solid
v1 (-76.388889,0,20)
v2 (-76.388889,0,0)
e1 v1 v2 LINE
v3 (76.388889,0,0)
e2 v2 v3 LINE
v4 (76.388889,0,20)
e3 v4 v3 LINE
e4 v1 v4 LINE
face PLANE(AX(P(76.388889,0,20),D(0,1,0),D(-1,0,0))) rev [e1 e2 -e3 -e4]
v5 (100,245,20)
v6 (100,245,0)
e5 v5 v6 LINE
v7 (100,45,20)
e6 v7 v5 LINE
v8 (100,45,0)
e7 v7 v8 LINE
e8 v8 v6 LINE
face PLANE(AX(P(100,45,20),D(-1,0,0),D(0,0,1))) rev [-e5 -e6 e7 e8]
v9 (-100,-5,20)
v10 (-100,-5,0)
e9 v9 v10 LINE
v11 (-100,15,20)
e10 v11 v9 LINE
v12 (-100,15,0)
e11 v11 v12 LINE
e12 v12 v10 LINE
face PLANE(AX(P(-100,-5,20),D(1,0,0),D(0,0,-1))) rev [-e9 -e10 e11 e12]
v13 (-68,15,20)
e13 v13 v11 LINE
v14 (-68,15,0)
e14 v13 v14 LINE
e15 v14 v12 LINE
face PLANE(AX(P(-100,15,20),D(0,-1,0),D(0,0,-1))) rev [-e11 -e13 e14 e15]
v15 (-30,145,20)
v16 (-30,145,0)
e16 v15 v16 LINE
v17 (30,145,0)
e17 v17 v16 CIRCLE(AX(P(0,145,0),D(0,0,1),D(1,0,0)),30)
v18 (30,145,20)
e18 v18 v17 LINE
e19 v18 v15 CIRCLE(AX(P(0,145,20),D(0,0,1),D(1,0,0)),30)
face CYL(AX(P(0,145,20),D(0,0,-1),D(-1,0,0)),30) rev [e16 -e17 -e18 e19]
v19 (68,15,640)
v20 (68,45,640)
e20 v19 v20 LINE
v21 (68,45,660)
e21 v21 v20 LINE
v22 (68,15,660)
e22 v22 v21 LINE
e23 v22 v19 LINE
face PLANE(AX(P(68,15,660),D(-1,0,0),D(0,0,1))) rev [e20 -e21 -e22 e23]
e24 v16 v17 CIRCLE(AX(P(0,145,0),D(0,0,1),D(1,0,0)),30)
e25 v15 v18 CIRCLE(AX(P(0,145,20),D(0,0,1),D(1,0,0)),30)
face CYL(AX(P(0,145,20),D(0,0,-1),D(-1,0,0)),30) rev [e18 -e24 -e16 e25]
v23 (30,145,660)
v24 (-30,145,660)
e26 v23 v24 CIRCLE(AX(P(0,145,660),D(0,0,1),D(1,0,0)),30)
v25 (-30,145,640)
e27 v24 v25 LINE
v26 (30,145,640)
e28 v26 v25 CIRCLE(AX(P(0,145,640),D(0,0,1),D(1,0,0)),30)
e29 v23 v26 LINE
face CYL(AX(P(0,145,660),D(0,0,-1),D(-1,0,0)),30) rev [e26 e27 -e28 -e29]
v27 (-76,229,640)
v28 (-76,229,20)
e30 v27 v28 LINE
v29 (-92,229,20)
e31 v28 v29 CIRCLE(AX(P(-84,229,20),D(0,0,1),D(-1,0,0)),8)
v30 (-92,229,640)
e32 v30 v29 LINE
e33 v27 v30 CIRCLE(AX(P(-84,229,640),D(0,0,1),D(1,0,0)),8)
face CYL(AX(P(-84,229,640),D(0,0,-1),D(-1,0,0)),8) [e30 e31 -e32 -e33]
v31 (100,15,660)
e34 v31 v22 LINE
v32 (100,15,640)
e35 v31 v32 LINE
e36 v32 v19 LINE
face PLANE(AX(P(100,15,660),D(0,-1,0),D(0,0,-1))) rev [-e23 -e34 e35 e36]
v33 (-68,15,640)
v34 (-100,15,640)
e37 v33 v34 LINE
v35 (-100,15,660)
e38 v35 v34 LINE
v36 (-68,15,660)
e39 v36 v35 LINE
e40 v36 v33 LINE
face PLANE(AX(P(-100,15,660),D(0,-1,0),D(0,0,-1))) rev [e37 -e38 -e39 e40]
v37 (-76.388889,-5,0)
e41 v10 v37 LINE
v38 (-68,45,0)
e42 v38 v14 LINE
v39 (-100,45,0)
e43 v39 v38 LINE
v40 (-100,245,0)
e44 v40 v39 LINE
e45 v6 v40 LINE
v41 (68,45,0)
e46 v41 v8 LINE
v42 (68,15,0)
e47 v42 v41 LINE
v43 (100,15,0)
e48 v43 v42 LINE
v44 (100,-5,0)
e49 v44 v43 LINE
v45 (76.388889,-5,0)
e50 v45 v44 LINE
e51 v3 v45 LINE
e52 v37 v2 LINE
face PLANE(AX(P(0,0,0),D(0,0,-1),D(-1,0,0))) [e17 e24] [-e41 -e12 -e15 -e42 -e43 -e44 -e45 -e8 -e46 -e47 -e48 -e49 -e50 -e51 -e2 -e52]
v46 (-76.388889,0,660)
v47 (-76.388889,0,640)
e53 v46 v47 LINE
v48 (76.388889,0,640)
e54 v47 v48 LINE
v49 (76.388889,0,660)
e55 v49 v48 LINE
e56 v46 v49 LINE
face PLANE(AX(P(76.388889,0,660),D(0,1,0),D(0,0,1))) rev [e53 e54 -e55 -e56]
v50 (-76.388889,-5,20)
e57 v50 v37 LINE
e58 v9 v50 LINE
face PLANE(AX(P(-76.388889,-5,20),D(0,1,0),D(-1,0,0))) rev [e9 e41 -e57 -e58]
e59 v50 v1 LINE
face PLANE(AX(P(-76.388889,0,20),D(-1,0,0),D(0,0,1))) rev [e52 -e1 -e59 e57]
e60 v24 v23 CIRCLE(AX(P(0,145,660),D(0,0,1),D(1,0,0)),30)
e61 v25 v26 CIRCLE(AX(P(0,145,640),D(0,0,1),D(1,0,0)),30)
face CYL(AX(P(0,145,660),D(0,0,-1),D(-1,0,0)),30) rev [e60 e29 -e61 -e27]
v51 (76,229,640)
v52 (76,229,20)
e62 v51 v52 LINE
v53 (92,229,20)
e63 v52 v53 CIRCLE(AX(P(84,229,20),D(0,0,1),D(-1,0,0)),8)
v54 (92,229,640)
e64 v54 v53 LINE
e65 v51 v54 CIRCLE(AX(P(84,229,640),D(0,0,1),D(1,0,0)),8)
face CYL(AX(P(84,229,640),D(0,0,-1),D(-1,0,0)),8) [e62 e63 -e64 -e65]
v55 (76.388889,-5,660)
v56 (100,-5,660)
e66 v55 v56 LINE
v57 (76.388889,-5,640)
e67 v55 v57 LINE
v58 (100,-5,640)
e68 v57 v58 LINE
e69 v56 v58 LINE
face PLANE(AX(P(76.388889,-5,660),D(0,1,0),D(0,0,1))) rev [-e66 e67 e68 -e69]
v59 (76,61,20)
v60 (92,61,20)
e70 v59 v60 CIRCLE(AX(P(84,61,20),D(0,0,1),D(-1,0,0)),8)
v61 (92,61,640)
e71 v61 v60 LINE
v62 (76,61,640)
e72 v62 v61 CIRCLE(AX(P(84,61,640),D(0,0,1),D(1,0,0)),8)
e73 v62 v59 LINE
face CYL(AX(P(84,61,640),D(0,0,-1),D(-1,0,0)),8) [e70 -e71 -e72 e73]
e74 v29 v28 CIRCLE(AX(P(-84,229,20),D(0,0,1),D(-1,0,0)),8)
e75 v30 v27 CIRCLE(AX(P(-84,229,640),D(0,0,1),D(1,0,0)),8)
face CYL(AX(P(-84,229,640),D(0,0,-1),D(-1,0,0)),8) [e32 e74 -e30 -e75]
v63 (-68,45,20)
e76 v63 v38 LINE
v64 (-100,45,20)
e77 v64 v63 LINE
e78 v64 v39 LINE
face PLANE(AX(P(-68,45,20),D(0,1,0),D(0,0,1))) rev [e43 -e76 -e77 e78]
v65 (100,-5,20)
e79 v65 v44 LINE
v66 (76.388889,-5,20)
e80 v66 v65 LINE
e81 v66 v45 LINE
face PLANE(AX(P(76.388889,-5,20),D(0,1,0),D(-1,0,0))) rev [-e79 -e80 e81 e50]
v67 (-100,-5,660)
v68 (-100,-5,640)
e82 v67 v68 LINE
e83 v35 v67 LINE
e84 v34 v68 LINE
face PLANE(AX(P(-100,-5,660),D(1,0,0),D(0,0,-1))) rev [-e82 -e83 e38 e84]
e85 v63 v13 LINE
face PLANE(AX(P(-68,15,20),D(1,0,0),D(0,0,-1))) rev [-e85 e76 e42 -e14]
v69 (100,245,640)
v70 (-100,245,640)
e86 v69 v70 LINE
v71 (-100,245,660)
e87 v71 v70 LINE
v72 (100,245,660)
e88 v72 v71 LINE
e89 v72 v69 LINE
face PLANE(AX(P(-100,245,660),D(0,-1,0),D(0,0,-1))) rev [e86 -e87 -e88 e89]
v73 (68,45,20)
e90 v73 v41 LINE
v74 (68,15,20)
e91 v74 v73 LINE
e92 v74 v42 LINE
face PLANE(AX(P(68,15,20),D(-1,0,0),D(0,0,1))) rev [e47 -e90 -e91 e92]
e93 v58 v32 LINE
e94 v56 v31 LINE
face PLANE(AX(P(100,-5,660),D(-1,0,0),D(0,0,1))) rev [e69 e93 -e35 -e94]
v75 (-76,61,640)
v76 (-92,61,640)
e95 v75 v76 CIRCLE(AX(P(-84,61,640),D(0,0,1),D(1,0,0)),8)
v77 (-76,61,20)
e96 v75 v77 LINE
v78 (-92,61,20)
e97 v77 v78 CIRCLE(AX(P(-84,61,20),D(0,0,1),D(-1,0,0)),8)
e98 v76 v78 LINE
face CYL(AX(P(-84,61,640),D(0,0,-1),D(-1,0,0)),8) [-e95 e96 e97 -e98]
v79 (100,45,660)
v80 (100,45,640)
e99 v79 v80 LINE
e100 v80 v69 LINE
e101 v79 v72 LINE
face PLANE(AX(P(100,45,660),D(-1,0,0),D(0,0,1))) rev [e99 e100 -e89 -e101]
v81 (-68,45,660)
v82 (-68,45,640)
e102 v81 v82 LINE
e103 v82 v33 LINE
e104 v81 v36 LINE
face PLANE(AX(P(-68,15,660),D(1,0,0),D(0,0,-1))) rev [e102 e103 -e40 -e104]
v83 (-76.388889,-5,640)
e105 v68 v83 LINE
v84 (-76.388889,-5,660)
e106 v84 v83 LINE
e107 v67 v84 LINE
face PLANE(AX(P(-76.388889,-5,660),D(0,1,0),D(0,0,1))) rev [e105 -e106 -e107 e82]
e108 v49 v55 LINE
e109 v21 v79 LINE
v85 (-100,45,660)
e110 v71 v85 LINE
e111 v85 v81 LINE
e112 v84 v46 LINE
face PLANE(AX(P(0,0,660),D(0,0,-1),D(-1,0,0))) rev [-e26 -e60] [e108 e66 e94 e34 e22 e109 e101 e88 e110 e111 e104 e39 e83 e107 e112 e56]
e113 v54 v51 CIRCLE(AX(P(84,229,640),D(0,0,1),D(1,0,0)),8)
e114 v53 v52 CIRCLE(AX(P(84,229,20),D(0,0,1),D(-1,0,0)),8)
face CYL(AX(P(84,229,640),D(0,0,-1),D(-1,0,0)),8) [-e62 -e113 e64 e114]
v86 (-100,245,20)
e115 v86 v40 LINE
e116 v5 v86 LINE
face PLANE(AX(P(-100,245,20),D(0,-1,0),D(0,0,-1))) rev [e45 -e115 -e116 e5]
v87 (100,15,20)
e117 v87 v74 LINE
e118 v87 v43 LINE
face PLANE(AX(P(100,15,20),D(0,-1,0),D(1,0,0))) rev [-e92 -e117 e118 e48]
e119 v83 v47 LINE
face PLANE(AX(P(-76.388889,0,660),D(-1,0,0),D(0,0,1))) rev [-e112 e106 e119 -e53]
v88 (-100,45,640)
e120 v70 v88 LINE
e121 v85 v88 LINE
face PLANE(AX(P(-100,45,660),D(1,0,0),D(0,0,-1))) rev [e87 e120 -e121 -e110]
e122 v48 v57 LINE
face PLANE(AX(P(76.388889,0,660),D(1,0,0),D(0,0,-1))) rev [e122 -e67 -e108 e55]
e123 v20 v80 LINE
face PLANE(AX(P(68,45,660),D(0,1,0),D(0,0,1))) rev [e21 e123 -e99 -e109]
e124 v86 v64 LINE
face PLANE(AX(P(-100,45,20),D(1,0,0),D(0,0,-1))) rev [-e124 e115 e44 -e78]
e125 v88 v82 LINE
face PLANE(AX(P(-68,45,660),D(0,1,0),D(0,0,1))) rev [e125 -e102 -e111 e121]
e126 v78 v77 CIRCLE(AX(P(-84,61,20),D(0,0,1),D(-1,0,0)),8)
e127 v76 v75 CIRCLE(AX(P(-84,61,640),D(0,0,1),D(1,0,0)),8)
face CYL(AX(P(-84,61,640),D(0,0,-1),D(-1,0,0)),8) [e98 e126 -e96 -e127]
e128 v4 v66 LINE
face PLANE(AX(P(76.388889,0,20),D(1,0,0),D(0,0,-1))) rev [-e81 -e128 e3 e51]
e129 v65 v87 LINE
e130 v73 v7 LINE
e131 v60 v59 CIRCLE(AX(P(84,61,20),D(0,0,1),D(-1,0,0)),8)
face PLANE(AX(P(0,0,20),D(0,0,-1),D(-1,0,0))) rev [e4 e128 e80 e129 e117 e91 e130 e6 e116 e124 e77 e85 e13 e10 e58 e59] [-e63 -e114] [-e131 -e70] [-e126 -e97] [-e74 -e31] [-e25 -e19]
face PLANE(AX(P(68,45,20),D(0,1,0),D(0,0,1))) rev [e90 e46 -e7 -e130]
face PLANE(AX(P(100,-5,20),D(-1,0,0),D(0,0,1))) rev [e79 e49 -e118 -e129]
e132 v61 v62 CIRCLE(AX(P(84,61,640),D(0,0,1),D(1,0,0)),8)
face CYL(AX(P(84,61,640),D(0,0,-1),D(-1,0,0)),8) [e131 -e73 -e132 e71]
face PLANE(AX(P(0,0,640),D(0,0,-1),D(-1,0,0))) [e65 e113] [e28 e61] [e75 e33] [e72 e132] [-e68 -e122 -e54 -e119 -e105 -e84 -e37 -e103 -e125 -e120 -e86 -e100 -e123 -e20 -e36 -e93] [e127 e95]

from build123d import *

# Parameters (mm, degrees)
SKETCH1_R           = 30
BOSS_EXTRUDE1_DEPTH = 20
SKETCH2_R           = 8
BOSS_EXTRUDE2_DEPTH = 620
SKETCH3_R           = 30
BOSS_EXTRUDE3_DEPTH = 20


with BuildPart() as part:
    # Sketch1 → Boss-Extrude1 (new body)
    with BuildSketch(Plane.XY):
        Polygon((76.388888889, 0), (-76.388888889, 0), (-76.388888889, -5), (-100, -5), (-100, 15), (-68, 15), (-68, 45), (-100, 45), (-100, 245), (100, 245), (100, 45), (68, 45), (68, 15), (100, 15), (100, -5), (76.388888889, -5), align=None)
        with Locations((0, 145)):
            Circle(SKETCH1_R, mode=Mode.SUBTRACT)
    extrude(amount=BOSS_EXTRUDE1_DEPTH)

    # Sketch2 → Boss-Extrude2 (add)
    with BuildSketch(Plane.XY.offset(20)):
        with Locations(Location((-84, 229, 0), (0, 0, 180))):
            Circle(SKETCH2_R)
        with Locations(Location((84, 229, 0), (0, 0, 180))):
            Circle(SKETCH2_R)
        with Locations(Location((84, 61, 0), (0, 0, 180))):
            Circle(SKETCH2_R)
        with Locations(Location((-84, 61, 0), (0, 0, 180))):
            Circle(SKETCH2_R)
    extrude(amount=BOSS_EXTRUDE2_DEPTH)

    # Sketch3 → Boss-Extrude3 (add)
    with BuildSketch(Plane.XY.offset(640)):
        Polygon((76.388888889, 0), (-76.388888889, 0), (-76.388888889, -5), (-100, -5), (-100, 15), (-68, 15), (-68, 45), (-100, 45), (-100, 245), (100, 245), (100, 45), (68, 45), (68, 15), (100, 15), (100, -5), (76.388888889, -5), align=None)
        with Locations((0, 145)):
            Circle(SKETCH3_R, mode=Mode.SUBTRACT)
    extrude(amount=BOSS_EXTRUDE3_DEPTH)


solid = part.part
